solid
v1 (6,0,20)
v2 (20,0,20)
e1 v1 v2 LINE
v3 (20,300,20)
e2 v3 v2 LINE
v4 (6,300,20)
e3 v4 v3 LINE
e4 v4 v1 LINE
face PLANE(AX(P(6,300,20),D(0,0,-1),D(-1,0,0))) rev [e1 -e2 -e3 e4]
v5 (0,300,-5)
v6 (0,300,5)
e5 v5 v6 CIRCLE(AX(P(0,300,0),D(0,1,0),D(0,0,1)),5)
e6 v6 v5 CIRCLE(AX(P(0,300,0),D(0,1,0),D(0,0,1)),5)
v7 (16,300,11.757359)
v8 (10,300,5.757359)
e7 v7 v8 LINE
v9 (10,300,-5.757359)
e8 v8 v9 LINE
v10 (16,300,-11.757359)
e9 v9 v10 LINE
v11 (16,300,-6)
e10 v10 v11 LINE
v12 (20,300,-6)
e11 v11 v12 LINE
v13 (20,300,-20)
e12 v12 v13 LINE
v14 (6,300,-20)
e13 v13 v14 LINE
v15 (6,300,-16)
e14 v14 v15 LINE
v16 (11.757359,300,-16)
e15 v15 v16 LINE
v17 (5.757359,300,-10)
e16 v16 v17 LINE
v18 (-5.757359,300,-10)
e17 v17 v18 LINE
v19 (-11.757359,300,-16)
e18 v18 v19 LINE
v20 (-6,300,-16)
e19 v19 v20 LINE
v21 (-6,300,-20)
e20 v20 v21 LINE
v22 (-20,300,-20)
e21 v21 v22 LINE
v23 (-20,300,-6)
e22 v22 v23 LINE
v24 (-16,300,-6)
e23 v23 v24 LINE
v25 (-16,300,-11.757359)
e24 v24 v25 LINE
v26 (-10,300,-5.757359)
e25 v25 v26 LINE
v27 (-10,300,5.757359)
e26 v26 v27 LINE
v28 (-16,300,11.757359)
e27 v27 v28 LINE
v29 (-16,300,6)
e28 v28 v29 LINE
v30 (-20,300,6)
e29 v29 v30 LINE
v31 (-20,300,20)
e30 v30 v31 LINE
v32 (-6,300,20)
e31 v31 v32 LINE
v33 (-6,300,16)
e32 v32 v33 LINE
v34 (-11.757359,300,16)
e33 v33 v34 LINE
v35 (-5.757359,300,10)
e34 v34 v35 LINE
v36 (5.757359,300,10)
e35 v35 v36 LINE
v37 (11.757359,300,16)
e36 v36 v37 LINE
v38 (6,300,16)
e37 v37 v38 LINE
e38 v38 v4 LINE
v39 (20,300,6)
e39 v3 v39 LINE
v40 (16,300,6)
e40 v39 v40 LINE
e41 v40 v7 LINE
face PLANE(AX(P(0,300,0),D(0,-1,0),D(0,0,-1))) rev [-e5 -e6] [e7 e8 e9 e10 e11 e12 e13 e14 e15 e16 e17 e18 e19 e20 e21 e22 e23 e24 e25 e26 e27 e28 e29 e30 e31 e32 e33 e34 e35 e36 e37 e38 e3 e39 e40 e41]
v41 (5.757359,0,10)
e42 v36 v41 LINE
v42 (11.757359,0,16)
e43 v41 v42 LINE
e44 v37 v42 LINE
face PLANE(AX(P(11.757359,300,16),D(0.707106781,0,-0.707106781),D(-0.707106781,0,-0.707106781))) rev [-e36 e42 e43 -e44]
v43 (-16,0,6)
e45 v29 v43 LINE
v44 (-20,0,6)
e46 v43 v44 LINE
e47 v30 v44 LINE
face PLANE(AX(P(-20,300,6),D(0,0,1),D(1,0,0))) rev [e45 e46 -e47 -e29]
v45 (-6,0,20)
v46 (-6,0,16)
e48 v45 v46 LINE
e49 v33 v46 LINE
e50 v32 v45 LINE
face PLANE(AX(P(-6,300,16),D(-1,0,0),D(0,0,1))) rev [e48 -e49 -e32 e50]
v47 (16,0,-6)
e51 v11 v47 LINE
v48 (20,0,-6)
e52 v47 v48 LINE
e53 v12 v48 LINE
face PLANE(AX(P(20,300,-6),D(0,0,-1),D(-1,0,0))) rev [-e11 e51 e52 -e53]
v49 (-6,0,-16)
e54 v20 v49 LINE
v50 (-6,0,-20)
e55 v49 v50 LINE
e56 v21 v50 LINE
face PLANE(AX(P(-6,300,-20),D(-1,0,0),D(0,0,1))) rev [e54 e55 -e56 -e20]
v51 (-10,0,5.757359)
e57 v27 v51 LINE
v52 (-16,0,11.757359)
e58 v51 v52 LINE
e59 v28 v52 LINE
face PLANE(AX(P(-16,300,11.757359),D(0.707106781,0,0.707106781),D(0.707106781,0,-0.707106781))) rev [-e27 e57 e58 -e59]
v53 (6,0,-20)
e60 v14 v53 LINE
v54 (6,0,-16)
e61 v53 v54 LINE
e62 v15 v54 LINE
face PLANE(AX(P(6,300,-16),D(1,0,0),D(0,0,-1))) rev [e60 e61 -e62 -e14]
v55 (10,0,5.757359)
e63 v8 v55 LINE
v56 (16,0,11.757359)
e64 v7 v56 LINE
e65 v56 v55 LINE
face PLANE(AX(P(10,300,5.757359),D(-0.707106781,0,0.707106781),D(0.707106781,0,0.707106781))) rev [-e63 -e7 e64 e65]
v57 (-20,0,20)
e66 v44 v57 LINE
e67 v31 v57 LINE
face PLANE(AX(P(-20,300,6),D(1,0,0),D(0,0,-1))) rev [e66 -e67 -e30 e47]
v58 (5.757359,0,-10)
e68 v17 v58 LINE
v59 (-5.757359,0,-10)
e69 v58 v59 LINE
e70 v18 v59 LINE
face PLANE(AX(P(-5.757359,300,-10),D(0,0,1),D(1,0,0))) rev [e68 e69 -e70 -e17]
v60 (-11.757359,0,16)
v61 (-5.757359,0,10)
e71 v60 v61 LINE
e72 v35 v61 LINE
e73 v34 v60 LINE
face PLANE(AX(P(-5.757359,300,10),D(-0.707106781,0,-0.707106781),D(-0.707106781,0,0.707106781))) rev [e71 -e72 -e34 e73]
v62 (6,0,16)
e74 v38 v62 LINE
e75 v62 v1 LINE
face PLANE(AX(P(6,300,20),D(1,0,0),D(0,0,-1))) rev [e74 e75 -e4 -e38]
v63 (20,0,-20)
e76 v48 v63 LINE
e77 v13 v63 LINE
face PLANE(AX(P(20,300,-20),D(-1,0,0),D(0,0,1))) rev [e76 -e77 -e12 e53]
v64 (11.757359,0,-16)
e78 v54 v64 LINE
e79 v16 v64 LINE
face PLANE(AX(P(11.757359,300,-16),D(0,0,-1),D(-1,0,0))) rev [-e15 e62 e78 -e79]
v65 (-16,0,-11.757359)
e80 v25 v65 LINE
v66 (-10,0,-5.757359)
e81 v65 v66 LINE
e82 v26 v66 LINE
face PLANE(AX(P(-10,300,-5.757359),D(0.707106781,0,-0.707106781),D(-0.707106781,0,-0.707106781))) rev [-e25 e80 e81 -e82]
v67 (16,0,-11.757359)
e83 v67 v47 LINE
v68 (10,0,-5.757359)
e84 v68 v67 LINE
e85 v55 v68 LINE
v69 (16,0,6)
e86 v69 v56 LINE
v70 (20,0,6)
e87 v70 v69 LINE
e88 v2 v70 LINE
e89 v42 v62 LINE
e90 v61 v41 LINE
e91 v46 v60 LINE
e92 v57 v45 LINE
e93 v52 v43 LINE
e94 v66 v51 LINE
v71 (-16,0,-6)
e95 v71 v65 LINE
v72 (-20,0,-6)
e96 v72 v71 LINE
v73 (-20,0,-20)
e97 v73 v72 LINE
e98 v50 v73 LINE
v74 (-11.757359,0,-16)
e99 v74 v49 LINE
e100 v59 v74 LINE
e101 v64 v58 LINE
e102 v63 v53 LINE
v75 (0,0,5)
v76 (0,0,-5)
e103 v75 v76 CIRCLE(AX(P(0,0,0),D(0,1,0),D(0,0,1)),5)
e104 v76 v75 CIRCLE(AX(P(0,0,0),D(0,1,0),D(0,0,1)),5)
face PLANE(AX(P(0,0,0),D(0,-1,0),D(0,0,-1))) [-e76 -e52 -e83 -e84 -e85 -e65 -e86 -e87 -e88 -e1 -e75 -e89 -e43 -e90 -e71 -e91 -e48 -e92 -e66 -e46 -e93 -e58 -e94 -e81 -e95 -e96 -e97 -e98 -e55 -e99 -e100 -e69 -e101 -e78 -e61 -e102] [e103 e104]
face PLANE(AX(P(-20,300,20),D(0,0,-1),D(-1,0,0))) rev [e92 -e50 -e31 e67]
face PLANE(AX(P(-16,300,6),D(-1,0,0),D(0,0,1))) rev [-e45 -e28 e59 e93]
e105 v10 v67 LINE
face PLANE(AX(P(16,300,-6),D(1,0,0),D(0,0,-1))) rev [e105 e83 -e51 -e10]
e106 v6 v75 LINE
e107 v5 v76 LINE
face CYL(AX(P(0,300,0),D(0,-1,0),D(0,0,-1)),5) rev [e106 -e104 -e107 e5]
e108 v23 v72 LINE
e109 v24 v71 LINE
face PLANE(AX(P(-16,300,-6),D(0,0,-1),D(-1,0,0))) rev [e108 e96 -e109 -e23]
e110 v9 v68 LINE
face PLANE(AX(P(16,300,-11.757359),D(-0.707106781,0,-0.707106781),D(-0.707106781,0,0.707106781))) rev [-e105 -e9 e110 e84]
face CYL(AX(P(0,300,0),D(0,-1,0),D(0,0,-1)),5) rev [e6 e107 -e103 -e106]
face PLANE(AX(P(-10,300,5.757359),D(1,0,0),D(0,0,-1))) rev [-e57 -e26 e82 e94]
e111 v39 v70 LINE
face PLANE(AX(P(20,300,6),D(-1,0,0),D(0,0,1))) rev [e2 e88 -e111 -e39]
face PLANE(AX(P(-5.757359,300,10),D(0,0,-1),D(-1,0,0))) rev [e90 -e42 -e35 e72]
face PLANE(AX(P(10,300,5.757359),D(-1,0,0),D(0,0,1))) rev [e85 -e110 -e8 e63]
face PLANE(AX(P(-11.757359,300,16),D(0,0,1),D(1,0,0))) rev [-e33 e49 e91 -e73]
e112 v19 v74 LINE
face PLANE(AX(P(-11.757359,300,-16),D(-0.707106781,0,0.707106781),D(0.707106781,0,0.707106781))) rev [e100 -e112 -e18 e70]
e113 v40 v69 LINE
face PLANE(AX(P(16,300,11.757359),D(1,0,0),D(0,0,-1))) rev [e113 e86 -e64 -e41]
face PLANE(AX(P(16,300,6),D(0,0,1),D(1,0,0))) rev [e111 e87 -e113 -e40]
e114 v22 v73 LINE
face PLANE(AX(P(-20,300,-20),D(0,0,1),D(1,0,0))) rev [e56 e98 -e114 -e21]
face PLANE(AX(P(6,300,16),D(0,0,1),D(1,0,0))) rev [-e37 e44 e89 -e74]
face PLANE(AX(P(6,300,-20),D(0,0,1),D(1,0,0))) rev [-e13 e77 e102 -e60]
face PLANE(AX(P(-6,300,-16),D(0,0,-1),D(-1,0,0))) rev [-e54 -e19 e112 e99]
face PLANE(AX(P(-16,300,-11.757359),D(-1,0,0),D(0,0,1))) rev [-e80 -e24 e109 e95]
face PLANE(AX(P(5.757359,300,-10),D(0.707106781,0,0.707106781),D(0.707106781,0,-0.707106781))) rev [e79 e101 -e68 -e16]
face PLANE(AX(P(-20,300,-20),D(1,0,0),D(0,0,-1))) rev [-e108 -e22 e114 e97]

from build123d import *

# Parameters (mm, degrees)
SKETCH1_R           = 5
BOSS_EXTRUDE1_DEPTH = 300


with BuildPart() as part:
    # Sketch1 → Boss-Extrude1 (new body)
    with BuildSketch(Plane(origin=(0, 0, 0), x_dir=(1, 0, 0), z_dir=(0, 1, 0))):
        Polygon((-6, 20), (-6, 16), (-11.757359313, 16), (-5.757359313, 10), (5.757359313, 10), (11.757359313, 16), (6, 16), (6, 20), (20, 20), (20, 6), (16, 6), (16, 11.757359313), (10, 5.757359313), (10, -5.757359313), (16, -11.757359313), (16, -6), (20, -6), (20, -20), (6, -20), (6, -16), (11.757359313, -16), (5.757359313, -10), (-5.757359313, -10), (-11.757359313, -16), (-6, -16), (-6, -20), (-20, -20), (-20, -6), (-16, -6), (-16, -11.757359313), (-10, -5.757359313), (-10, 5.757359313), (-16, 11.757359313), (-16, 6), (-20, 6), (-20, 20), align=None)
        with Locations(Location((0, 0, 0), (0, 0, 270))):
            Circle(SKETCH1_R, mode=Mode.SUBTRACT)
    extrude(amount=BOSS_EXTRUDE1_DEPTH)


solid = part.part
